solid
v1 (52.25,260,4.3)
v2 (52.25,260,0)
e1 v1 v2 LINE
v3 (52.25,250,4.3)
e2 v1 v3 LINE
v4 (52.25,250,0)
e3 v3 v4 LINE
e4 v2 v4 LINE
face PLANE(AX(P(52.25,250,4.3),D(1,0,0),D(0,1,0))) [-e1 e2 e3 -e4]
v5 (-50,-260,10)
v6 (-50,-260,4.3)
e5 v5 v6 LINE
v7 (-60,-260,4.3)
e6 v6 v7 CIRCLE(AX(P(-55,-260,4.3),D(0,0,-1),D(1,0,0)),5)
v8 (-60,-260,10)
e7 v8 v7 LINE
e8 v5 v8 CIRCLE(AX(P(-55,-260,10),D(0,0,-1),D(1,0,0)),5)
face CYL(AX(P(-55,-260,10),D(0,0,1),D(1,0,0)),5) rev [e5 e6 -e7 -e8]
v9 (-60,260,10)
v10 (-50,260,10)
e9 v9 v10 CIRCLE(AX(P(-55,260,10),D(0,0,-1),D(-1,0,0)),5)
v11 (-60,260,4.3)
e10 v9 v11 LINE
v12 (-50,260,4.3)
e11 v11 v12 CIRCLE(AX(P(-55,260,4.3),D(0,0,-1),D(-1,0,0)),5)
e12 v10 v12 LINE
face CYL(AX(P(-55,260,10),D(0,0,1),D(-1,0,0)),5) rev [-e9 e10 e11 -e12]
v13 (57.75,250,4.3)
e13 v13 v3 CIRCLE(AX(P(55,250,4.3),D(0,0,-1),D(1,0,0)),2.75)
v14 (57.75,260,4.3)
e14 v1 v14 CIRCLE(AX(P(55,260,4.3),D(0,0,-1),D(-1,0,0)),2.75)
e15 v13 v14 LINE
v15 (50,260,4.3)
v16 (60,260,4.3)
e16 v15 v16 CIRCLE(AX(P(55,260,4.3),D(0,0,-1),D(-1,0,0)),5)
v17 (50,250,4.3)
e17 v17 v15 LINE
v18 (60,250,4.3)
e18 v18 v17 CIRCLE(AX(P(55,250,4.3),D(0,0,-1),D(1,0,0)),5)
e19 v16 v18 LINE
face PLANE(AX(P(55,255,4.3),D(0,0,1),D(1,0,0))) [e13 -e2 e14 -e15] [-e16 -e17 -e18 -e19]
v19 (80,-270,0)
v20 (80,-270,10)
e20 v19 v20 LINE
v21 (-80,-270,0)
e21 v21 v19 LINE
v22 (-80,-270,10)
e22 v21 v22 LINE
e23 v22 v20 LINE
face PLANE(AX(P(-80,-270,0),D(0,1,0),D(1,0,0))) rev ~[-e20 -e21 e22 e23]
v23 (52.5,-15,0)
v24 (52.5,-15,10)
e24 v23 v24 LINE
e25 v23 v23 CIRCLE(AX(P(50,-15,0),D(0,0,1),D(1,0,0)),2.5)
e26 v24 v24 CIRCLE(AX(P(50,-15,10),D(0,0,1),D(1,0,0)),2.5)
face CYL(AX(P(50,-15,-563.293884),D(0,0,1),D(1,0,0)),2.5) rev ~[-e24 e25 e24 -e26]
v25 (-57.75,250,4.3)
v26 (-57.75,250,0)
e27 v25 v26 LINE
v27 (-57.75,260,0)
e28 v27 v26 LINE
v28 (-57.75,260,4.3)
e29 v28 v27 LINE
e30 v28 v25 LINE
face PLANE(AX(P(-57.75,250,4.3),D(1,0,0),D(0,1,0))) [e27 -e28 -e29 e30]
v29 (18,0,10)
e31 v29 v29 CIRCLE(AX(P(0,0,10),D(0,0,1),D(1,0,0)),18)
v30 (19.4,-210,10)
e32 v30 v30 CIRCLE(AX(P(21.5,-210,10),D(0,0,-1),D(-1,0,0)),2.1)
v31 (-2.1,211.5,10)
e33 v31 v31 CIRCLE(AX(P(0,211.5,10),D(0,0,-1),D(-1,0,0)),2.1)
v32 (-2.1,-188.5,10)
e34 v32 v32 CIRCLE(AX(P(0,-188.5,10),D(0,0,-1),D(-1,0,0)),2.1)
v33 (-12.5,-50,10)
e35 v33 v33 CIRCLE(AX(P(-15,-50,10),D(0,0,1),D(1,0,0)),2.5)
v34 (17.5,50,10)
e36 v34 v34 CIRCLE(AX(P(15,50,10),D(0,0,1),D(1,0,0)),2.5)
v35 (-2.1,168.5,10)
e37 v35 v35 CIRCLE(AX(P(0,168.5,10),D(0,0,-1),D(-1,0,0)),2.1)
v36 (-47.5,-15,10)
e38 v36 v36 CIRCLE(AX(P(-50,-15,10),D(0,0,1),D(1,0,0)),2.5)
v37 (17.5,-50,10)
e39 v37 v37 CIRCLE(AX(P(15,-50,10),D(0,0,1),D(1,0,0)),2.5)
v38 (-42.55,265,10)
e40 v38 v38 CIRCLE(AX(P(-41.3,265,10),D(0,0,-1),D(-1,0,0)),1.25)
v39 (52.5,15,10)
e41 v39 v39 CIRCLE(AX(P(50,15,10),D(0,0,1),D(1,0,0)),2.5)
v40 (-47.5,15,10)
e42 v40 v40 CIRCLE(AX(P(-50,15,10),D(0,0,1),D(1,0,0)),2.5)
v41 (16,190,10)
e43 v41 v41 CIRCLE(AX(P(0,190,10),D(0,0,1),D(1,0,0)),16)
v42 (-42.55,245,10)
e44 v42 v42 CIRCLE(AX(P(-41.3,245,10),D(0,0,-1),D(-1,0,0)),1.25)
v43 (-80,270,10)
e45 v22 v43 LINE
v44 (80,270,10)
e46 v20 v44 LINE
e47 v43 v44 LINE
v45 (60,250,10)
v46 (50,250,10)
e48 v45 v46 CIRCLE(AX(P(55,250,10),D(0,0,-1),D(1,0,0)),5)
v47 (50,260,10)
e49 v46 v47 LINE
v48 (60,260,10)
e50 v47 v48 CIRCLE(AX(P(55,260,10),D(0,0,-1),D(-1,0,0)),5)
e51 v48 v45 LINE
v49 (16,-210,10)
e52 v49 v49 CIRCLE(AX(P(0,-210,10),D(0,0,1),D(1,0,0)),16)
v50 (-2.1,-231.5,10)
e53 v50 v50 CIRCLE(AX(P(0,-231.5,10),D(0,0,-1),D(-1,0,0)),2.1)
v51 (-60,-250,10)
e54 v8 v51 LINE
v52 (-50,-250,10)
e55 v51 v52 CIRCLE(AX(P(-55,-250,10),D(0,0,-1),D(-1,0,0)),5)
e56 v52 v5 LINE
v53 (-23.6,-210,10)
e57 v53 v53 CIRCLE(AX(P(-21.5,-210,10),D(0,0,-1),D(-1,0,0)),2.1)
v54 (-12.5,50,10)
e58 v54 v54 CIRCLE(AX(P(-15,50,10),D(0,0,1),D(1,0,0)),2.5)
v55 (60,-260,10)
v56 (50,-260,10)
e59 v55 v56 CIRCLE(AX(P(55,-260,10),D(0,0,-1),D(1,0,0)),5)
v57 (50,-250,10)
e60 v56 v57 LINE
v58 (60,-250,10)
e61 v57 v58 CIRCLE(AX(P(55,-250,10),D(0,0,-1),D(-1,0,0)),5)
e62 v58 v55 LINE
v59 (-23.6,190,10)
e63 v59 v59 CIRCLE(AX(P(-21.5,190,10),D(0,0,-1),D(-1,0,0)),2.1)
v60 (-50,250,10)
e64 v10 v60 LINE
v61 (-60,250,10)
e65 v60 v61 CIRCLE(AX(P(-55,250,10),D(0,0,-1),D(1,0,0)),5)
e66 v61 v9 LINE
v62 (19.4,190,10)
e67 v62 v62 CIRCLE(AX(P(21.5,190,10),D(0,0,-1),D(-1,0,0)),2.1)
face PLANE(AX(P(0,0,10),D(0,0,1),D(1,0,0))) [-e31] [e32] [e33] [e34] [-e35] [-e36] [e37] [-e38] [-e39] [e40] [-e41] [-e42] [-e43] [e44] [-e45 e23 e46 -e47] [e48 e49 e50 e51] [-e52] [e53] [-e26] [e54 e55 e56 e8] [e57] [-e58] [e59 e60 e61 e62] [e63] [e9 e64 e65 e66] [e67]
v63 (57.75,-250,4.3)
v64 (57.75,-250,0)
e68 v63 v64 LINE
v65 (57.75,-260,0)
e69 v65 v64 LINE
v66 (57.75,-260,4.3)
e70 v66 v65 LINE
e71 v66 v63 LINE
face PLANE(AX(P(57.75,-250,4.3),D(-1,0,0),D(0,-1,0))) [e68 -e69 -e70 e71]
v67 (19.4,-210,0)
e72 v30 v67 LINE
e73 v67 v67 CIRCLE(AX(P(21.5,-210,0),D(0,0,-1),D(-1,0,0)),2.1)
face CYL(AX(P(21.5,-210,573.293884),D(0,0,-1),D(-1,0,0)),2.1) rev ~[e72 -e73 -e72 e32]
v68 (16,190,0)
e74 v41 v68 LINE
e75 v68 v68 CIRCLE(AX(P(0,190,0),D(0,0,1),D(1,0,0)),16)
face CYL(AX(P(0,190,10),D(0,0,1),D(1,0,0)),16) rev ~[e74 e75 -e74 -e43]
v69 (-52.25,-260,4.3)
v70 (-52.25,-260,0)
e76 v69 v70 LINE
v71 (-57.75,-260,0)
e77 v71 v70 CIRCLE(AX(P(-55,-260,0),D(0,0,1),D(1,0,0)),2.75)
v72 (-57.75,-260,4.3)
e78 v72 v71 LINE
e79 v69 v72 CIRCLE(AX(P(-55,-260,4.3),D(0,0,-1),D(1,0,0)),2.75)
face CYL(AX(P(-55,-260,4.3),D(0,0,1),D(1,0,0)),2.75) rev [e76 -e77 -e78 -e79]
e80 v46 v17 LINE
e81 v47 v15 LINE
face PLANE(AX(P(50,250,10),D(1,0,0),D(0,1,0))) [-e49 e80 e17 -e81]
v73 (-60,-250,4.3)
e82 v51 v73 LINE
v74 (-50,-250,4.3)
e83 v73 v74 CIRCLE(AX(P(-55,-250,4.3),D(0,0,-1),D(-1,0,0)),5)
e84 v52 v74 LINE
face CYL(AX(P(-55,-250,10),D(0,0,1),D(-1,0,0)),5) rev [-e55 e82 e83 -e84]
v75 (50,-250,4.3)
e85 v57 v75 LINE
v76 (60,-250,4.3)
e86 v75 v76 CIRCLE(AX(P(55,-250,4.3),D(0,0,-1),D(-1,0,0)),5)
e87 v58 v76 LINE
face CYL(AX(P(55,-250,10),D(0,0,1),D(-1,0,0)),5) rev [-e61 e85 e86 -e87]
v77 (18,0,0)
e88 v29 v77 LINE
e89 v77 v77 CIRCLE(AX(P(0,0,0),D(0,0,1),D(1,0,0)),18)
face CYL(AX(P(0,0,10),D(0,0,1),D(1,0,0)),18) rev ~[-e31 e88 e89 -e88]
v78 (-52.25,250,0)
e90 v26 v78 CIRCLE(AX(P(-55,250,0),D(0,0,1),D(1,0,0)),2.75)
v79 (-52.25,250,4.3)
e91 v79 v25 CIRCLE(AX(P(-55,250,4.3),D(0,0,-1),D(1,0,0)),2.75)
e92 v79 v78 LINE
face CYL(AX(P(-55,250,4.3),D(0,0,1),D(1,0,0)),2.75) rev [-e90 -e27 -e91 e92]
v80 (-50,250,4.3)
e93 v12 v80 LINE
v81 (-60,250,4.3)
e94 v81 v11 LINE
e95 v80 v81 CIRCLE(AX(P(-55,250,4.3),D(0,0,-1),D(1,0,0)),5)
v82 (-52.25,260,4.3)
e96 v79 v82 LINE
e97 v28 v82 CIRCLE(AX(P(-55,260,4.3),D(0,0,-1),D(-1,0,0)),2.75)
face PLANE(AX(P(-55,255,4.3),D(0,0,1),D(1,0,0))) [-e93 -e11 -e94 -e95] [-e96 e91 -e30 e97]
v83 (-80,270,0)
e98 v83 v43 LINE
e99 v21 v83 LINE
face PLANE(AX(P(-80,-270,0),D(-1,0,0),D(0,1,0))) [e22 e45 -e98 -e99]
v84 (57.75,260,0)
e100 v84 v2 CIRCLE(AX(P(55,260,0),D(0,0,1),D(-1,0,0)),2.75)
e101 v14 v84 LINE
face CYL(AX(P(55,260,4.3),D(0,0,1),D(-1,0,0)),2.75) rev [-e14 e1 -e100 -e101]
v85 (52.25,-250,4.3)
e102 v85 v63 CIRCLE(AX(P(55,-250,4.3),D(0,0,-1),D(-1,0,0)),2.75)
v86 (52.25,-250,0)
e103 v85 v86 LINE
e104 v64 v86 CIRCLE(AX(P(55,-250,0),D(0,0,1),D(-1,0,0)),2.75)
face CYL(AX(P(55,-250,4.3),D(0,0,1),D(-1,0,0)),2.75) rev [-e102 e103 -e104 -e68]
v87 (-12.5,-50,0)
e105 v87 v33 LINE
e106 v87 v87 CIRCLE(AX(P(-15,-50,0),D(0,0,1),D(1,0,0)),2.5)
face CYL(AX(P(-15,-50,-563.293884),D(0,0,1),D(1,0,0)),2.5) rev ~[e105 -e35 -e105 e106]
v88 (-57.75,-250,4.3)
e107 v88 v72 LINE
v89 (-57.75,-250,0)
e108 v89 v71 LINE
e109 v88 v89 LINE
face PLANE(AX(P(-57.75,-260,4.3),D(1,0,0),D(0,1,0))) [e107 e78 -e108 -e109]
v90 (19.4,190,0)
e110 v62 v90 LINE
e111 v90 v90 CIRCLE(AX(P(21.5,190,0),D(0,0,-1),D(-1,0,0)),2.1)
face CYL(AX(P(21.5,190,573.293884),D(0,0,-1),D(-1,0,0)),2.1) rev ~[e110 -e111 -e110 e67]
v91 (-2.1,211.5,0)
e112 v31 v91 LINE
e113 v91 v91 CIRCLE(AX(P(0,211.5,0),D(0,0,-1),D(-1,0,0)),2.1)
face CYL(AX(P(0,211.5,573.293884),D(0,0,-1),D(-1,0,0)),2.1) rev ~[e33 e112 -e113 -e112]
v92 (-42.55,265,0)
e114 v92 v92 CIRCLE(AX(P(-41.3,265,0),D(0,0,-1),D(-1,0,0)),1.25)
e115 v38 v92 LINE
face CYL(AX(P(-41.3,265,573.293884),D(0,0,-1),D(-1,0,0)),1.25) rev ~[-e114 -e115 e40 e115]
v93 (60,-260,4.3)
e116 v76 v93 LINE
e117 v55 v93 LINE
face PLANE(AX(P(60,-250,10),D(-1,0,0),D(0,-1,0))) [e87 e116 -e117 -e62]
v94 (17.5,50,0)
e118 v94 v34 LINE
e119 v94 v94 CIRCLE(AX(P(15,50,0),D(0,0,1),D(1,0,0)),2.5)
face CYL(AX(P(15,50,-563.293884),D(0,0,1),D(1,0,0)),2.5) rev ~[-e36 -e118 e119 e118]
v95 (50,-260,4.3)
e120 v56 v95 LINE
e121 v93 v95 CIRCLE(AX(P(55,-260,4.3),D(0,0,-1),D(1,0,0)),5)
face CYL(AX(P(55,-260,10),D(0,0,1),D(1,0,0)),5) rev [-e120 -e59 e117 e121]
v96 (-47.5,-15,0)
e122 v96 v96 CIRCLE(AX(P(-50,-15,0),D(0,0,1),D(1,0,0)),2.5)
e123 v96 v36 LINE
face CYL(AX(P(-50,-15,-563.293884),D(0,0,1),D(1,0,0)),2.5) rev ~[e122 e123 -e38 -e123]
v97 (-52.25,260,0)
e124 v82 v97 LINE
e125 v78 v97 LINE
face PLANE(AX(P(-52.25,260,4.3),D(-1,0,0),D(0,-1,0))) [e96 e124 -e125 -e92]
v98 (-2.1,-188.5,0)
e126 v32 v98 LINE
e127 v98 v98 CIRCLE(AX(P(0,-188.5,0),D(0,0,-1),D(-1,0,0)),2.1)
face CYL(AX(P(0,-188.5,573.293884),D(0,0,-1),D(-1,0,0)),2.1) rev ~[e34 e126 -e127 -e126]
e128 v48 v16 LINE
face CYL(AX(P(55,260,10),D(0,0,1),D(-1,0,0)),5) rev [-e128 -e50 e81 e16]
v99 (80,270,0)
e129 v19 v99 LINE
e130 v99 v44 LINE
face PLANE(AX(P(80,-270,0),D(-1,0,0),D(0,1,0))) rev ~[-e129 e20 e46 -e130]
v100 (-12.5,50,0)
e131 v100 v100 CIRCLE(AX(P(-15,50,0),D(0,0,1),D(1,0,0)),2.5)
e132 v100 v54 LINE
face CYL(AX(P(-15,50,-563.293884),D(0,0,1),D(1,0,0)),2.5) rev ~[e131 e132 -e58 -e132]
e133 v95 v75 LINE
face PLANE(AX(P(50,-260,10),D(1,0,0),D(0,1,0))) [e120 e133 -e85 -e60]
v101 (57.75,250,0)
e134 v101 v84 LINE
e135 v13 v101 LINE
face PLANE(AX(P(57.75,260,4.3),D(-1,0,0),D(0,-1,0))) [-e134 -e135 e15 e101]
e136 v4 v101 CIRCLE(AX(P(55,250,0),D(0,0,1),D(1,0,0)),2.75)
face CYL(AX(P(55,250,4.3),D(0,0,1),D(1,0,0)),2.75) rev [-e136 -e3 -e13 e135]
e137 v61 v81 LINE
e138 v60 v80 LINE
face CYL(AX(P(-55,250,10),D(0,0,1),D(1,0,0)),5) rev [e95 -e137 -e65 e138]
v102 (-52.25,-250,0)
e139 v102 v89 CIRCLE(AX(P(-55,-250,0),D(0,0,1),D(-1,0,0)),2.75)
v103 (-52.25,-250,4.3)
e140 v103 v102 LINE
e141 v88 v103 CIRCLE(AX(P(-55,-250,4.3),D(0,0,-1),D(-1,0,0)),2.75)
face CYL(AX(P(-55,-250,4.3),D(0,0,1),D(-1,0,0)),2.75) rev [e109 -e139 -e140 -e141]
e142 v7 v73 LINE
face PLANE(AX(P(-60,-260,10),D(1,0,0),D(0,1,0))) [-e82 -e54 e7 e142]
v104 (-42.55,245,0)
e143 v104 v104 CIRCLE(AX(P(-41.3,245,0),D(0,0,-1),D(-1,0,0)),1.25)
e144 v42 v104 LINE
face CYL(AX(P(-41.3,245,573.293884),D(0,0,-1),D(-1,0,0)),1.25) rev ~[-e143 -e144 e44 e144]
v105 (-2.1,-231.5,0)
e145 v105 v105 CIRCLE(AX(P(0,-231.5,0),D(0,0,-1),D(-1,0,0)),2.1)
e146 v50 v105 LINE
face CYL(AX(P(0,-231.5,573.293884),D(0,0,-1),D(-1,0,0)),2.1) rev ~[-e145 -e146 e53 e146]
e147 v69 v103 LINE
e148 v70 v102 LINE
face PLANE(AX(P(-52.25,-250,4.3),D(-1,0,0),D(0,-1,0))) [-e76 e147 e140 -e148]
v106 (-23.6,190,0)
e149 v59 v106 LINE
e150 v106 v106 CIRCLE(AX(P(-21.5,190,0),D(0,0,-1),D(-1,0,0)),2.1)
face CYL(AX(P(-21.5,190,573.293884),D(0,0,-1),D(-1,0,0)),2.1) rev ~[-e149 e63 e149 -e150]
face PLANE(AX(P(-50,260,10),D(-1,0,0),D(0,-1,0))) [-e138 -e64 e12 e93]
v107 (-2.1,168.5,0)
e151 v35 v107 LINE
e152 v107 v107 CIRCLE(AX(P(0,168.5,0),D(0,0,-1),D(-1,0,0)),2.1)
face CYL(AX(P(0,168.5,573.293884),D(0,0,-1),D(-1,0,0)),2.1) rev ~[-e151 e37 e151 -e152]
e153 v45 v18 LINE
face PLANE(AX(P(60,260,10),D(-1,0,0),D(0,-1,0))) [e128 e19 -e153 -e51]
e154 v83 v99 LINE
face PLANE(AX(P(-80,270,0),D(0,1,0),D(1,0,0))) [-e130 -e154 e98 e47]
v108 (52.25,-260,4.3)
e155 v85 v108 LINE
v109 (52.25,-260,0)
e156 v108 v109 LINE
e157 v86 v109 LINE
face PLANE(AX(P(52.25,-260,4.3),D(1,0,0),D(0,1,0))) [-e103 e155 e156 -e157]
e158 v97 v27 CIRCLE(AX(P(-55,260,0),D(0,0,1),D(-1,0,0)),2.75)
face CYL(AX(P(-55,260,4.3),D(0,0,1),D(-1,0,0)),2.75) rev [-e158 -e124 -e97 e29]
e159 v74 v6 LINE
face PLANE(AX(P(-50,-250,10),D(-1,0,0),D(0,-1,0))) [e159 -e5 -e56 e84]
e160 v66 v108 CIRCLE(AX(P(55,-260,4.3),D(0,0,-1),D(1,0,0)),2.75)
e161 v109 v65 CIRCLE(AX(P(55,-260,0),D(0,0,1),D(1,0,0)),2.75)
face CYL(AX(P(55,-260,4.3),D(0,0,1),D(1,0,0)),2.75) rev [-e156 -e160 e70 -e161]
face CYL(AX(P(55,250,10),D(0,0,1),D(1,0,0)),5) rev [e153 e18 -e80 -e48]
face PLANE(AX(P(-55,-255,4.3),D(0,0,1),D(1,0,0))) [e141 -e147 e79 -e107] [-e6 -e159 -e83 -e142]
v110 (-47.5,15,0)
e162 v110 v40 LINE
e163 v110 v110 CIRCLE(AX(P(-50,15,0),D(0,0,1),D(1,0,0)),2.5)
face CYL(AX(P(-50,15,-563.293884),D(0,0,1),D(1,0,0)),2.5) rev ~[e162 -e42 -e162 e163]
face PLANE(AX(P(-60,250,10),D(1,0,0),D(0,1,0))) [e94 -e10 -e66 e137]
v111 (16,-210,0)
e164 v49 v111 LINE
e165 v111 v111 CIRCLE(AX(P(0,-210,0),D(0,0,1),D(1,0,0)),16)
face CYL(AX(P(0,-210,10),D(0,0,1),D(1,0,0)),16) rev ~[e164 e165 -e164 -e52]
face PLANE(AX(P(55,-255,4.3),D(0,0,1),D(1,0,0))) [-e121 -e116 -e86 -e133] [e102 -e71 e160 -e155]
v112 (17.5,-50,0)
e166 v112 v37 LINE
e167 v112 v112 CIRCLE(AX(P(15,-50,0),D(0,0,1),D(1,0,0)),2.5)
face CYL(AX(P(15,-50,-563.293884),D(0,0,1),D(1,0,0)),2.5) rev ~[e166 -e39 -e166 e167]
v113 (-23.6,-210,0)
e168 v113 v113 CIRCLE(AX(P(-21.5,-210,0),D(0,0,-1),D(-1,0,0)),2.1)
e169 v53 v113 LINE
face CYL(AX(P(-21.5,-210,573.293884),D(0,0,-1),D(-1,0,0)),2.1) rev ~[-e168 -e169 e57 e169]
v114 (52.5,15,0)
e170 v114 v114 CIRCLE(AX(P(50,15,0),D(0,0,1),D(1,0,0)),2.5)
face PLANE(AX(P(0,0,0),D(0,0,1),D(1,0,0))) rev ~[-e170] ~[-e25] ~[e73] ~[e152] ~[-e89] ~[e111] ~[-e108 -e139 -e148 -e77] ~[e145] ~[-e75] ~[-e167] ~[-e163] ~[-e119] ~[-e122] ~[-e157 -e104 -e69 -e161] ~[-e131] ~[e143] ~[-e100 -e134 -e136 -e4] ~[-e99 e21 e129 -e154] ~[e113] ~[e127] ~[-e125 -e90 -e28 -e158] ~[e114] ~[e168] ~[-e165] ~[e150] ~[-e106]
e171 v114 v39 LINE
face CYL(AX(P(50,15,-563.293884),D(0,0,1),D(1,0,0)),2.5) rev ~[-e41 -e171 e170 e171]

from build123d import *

# Parameters (mm, degrees)
SKETCH_1_W                = 160
SKETCH_1_H                = 540
EXTRUDE_1_DEPTH           = 10
SKETCH_2_R                = 16
CUT_EXTRUDE_1_DEPTH       = 282.780056072
SKETCH_3_R                = 18
CUT_EXTRUDE_2_DEPTH       = 282.780056072
HOLE_WIZARD_1_D           = 5.5
HOLE_WIZARD_1_CBORE_D     = 10
HOLE_WIZARD_1_CBORE_DEPTH = 5.7
HOLE_WIZARD_M5_1_D        = 4.2
HOLE_WIZARD_M5_2_D        = 4.2
HOLE_WIZARD_M5_3_D        = 4.2
HOLE_WIZARD_M3_1_D        = 2.5
HOLE_WIZARD_M6_2_D        = 5
CUT_EXTRUDE_3_DEPTH       = 5.7
CUT_EXTRUDE_4_DEPTH       = 282.660238585
HOLE_WIZARD_M6_3_D        = 5


with BuildPart() as part:
    # 草图1 → 凸台-拉伸1 (new body)
    with BuildSketch(Plane.XY):
        Rectangle(SKETCH_1_W, SKETCH_1_H)
    extrude(amount=EXTRUDE_1_DEPTH)

    # 草图2 → 切除-拉伸1 (cut, through all)
    with BuildSketch(Plane.XY.offset(10)):
        with Locations((0, 190)):
            Circle(SKETCH_2_R)
        with Locations((0, -210)):
            Circle(SKETCH_2_R)
    extrude(amount=-CUT_EXTRUDE_1_DEPTH, mode=Mode.SUBTRACT)

    # 草图3 → 切除-拉伸2 (cut, through all)
    with BuildSketch(Plane.XY.offset(10)):
        Circle(SKETCH_3_R)
    extrude(amount=-CUT_EXTRUDE_2_DEPTH, mode=Mode.SUBTRACT)

    # 打孔尺寸根据内六角圆柱头螺钉的类型1 (through all)
    with Locations(Plane.XY.offset(10)):
        with Locations((-55, 255), (55, 255), (55, -255), (-55, -255)):
            CounterBoreHole(HOLE_WIZARD_1_D / 2, HOLE_WIZARD_1_CBORE_D / 2, HOLE_WIZARD_1_CBORE_DEPTH)

    # M5 螺纹孔1 (through all)
    with Locations(Plane.XY.offset(10)):
        with Locations((0, 211.5)):
            Hole(HOLE_WIZARD_M5_1_D / 2)

    # M5 螺纹孔2 (through all)
    with Locations(Plane.XY.offset(10)):
        with Locations((0, -231.5)):
            Hole(HOLE_WIZARD_M5_2_D / 2)

    # M5 螺纹孔3 (through all)
    with Locations(Plane.XY.offset(10)):
        with Locations((21.5, -210), (-21.5, -210), (0, -188.5), (-21.5, 190), (21.5, 190), (0, 168.5)):
            Hole(HOLE_WIZARD_M5_3_D / 2)

    # M3 螺纹孔1 (through all)
    with Locations(Plane.XY.offset(10)):
        with Locations((-41.3, 265), (-41.3, 245)):
            Hole(HOLE_WIZARD_M3_1_D / 2)

    # M6 螺纹孔2 (through all)
    with Locations(Plane(origin=(0, 0, 0), x_dir=(-1, 0, 0), z_dir=(0, 0, -1))):
        with Locations((-50, 15), (-50, -15), (50, 15), (50, -15)):
            Hole(HOLE_WIZARD_M6_2_D / 2)

    # 草图24 → 切除-拉伸3 (cut)
    with BuildSketch(Plane.XY.offset(10)):
        with BuildLine():
            Line((-50, 260), (-50, 250))
            ThreePointArc((-50, 250), (-55, 245), (-60, 250))
            Line((-60, 250), (-60, 260))
            ThreePointArc((-60, 260), (-55, 265), (-50, 260))
        make_face()
        with BuildLine():
            Line((60, 260), (60, 250))
            ThreePointArc((60, 250), (55, 245), (50, 250))
            Line((50, 250), (50, 260))
            ThreePointArc((50, 260), (55, 265), (60, 260))
        make_face()
        with BuildLine():
            Line((-50, -250), (-50, -260))
            ThreePointArc((-50, -260), (-55, -265), (-60, -260))
            Line((-60, -260), (-60, -250))
            ThreePointArc((-60, -250), (-55, -245), (-50, -250))
        make_face()
        with BuildLine():
            Line((60, -250), (60, -260))
            ThreePointArc((60, -260), (55, -265), (50, -260))
            Line((50, -260), (50, -250))
            ThreePointArc((50, -250), (55, -245), (60, -250))
        make_face()
    extrude(amount=-CUT_EXTRUDE_3_DEPTH, mode=Mode.SUBTRACT)

    # 草图25 → 切除-拉伸4 (cut, through all)
    with BuildSketch(Plane.XY.offset(4.3)):
        with BuildLine():
            Line((-52.25, 260), (-52.25, 250))
            ThreePointArc((-52.25, 250), (-55, 247.25), (-57.75, 250))
            Line((-57.75, 250), (-57.75, 260))
            ThreePointArc((-57.75, 260), (-55, 262.75), (-52.25, 260))
        make_face()
        with BuildLine():
            Line((57.75, 260), (57.75, 250))
            ThreePointArc((57.75, 250), (55, 247.25), (52.25, 250))
            Line((52.25, 250), (52.25, 260))
            ThreePointArc((52.25, 260), (55, 262.75), (57.75, 260))
        make_face()
        with BuildLine():
            Line((-52.25, -250), (-52.25, -260))
            ThreePointArc((-52.25, -260), (-55, -262.75), (-57.75, -260))
            Line((-57.75, -260), (-57.75, -250))
            ThreePointArc((-57.75, -250), (-55, -247.25), (-52.25, -250))
        make_face()
        with BuildLine():
            Line((57.75, -250), (57.75, -260))
            ThreePointArc((57.75, -260), (55, -262.75), (52.25, -260))
            Line((52.25, -260), (52.25, -250))
            ThreePointArc((52.25, -250), (55, -247.25), (57.75, -250))
        make_face()
    extrude(amount=-CUT_EXTRUDE_4_DEPTH, mode=Mode.SUBTRACT)

    # M6 螺纹孔3 (through all)
    with Locations(Plane(origin=(0, 0, 0), x_dir=(-1, 0, 0), z_dir=(0, 0, -1))):
        with Locations((15, -50), (-15, -50), (-15, 50), (15, 50)):
            Hole(HOLE_WIZARD_M6_3_D / 2)


solid = part.part
